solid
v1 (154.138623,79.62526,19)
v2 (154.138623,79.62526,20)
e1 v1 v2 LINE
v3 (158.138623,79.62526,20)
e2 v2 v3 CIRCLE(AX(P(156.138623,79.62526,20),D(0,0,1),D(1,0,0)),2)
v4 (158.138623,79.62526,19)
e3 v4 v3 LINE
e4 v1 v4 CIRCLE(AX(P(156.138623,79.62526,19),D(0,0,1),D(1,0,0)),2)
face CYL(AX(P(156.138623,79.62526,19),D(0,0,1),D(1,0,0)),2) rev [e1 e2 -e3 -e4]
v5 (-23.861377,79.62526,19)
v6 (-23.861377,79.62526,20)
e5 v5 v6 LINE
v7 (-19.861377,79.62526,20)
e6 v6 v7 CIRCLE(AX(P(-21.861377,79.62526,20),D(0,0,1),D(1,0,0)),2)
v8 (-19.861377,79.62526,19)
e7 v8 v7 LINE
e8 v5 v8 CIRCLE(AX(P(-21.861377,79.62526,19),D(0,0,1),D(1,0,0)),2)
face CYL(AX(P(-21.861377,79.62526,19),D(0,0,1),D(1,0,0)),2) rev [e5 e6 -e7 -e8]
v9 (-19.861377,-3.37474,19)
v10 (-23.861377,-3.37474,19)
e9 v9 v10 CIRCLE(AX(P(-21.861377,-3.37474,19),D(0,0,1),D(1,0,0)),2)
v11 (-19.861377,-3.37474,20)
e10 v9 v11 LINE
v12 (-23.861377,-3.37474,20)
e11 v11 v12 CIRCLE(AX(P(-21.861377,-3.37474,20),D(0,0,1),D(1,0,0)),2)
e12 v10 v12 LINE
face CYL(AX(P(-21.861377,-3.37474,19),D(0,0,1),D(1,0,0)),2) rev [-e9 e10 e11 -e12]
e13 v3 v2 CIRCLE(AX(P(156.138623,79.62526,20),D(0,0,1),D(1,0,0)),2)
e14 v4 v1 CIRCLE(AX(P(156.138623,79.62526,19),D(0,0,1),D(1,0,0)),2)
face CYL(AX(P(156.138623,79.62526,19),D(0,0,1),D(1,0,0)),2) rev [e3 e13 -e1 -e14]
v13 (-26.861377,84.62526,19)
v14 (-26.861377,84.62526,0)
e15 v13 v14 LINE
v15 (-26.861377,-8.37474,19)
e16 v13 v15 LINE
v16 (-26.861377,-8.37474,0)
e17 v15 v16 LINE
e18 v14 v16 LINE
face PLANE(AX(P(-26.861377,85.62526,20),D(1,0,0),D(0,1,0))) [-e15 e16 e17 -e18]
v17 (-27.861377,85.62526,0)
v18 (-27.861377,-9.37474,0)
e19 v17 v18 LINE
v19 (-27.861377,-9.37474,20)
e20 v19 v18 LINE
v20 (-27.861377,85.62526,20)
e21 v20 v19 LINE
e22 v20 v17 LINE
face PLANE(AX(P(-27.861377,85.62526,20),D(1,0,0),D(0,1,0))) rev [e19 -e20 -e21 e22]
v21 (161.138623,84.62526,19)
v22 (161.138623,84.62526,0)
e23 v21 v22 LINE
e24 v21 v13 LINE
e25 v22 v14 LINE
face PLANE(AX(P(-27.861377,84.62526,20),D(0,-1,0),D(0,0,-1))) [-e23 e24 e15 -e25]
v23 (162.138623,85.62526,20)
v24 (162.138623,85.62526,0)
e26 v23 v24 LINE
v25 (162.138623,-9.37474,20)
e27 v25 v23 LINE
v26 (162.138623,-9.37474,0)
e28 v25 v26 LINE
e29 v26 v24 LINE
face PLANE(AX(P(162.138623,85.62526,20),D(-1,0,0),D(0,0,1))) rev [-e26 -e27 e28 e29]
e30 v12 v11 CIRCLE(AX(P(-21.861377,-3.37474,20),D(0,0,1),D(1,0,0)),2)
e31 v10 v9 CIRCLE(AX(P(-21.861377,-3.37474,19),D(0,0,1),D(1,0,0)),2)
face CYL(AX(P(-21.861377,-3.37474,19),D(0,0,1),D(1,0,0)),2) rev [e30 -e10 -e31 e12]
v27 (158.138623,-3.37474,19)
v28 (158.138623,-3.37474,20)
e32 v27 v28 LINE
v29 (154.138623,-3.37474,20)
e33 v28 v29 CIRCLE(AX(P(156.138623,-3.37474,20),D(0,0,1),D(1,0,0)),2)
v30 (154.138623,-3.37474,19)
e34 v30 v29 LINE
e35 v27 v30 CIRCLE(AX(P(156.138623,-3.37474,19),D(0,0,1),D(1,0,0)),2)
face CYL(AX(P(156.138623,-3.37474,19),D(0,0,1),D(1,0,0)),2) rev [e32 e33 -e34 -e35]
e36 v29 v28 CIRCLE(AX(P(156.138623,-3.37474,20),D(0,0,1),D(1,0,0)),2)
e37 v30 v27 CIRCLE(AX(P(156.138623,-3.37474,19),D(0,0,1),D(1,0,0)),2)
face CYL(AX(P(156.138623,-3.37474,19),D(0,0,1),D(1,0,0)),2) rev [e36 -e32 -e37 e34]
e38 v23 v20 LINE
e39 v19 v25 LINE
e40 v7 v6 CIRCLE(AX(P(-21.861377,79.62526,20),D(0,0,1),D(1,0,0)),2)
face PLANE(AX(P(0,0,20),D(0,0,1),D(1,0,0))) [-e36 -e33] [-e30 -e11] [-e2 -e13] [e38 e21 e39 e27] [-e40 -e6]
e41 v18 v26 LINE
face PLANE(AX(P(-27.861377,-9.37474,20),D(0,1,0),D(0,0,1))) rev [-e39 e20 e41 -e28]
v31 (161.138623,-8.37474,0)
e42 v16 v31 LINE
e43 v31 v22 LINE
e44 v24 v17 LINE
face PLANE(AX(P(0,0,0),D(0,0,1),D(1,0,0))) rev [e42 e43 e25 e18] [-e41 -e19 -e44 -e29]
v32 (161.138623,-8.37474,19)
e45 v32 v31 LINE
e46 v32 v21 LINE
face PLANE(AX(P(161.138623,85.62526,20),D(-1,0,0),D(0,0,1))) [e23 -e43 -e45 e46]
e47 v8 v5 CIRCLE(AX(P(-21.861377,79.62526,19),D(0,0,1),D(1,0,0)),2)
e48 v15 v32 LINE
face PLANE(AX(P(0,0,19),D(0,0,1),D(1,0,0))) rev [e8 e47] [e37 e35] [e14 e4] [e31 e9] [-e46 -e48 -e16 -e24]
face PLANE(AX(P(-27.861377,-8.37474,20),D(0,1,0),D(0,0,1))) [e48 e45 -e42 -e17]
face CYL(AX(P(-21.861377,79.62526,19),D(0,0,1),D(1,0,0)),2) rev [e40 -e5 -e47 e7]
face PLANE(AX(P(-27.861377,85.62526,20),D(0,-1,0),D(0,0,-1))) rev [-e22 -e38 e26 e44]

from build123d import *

# Parameters (mm, degrees)
SKETCH1_W           = 190
SKETCH1_H           = 95
BOSS_EXTRUDE1_DEPTH = 20
SHELL1_T            = -1
SKETCH2_W           = 146
SKETCH2_H           = 10
CUT_EXTRUDE1_DEPTH  = 1
SKETCH4_R           = 3.5
SKETCH4_W           = 9
SKETCH4_H           = 5.067595116
CUT_EXTRUDE2_DEPTH  = 10
SKETCH5_W           = 3
SKETCH5_H           = 2
CUT_EXTRUDE3_DEPTH  = 1
SKETCH6_R           = 2
CUT_EXTRUDE4_DEPTH  = 1
SKETCH8_W           = 3
SKETCH8_H           = 2
SKETCH8_W_2         = 27
SKETCH8_W_3         = 7
SKETCH8_W_4         = 17
SKETCH8_W_5         = 10
CUT_EXTRUDE5_DEPTH  = 1
SKETCH9_W           = 3
SKETCH9_H           = 2
SKETCH9_W_2         = 17
SKETCH9_W_3         = 6
SKETCH9_W_4         = 14
CUT_EXTRUDE6_DEPTH  = 1
SKETCH10_W          = 146
SKETCH10_H          = 12
BOSS_EXTRUDE2_DEPTH = 1
SKETCH11_R          = 3.5
SKETCH11_W          = 156
SKETCH11_H          = 11.148334169
SKETCH11_W_2        = 9
SKETCH11_H_2        = 5.067595116
BOSS_EXTRUDE3_DEPTH = 1
SKETCH12_W          = 22.5
SKETCH12_H          = 11
BOSS_EXTRUDE4_DEPTH = 1


with BuildPart() as part:
    # Sketch1 → Boss-Extrude1 (new body)
    with BuildSketch(Plane.XY):
        with Locations((67.138623448, 38.125260091)):
            Rectangle(SKETCH1_W, SKETCH1_H)
    extrude(amount=BOSS_EXTRUDE1_DEPTH)

    # Shell1
    shell1_openings = [part.faces().sort_by_distance(p)[0] for p in [
        (67.138623448, 38.125260091, 0),
    ]]
    offset(amount=SHELL1_T, openings=shell1_openings, kind=Kind.INTERSECTION)

    # Sketch2 → Cut-Extrude1 (cut)
    with BuildSketch(Plane(origin=(0, 85.625260091, 0), x_dir=(1, 0, 0), z_dir=(0, 1, 0))):
        Polygon((139.138623448, -9), (139.138623448, -8), (139.638623448, -8), (149.638623448, -8), (149.638623448, -19), (139.638623448, -19), (139.138623448, -19), (127.138623448, -19), (127.138623448, -9), align=None)
        with Locations((53.138623448, -14)):
            Rectangle(SKETCH2_W, SKETCH2_H)
    extrude(amount=-CUT_EXTRUDE1_DEPTH, mode=Mode.SUBTRACT)

    # Sketch4 → Cut-Extrude2 (cut)
    with BuildSketch(Plane.XZ.offset(9.374739909)):
        with Locations(Location((144.138623448, 6.5, 0), (0, 0, 270))):
            Circle(SKETCH4_R)
        Polygon((124.166122212, 9.851665831), (138.166122212, 9.851665831), (138.166122212, 19), (-17.833877788, 19), (-17.833877788, 9.851665831), (-14.833877788, 9.851665831), (-14.833877788, 7.851665831), (-11.833877788, 7.851665831), (-11.833877788, 9.851665831), (5.166122212, 9.851665831), (5.166122212, 7.851665831), (8.166122212, 7.851665831), (8.166122212, 9.851665831), (14.166122212, 9.851665831), (14.166122212, 7.851665831), (17.166122212, 7.851665831), (17.166122212, 9.851665831), (34.166122212, 9.851665831), (34.166122212, 7.851665831), (37.166122212, 7.851665831), (37.166122212, 9.851665831), (43.166122212, 9.851665831), (43.166122212, 7.851665831), (46.166122212, 7.851665831), (46.166122212, 9.851665831), (63.166122212, 9.851665831), (63.166122212, 7.851665831), (66.166122212, 7.851665831), (66.166122212, 9.851665831), (72.166122212, 9.851665831), (72.166122212, 7.851665831), (75.166122212, 7.851665831), (75.166122212, 9.851665831), (92.166122212, 9.851665831), (92.166122212, 7.851665831), (95.166122212, 7.851665831), (95.166122212, 9.851665831), (101.166122212, 9.851665831), (101.166122212, 7.851665831), (104.166122212, 7.851665831), (104.166122212, 9.851665831), (121.166122212, 9.851665831), (121.166122212, 7.851665831), (124.166122212, 7.851665831), align=None)
        with Locations((109.666122212, 4.317868273)):
            Rectangle(SKETCH4_W, SKETCH4_H)
    extrude(amount=-CUT_EXTRUDE2_DEPTH, mode=Mode.SUBTRACT)

    # Sketch5 → Cut-Extrude3 (cut)
    with BuildSketch(Plane(origin=(0, 85.625260091, 0), x_dir=(1, 0, 0), z_dir=(0, 1, 0))):
        with Locations((-15.361376552, -8)):
            Rectangle(SKETCH5_W, SKETCH5_H)
        with Locations((14.638623448, -8)):
            Rectangle(SKETCH5_W, SKETCH5_H)
        with Locations((24.638623448, -8)):
            Rectangle(SKETCH5_W, SKETCH5_H)
        with Locations((54.638623448, -8)):
            Rectangle(SKETCH5_W, SKETCH5_H)
        with Locations((64.638623448, -8)):
            Rectangle(SKETCH5_W, SKETCH5_H)
        with Locations((84.638623448, -8)):
            Rectangle(SKETCH5_W, SKETCH5_H)
        with Locations((94.638623448, -8)):
            Rectangle(SKETCH5_W, SKETCH5_H)
        with Locations((114.638623448, -8)):
            Rectangle(SKETCH5_W, SKETCH5_H)
    extrude(amount=-CUT_EXTRUDE3_DEPTH, mode=Mode.SUBTRACT)

    # Sketch6 → Cut-Extrude4 (cut)
    with BuildSketch(Plane.XY.offset(20)):
        with Locations((-21.861376552, -3.374739909)):
            Circle(SKETCH6_R)
        with Locations((-21.861376552, 79.625260091)):
            Circle(SKETCH6_R)
        with Locations((156.138623448, 79.625260091)):
            Circle(SKETCH6_R)
        with Locations((156.138623448, -3.374739909)):
            Circle(SKETCH6_R)
    extrude(amount=-CUT_EXTRUDE4_DEPTH, mode=Mode.SUBTRACT)

    # Sketch8 → Cut-Extrude5 (cut)
    with BuildSketch(Plane(origin=(0, 85.625260091, 0), x_dir=(1, 0, 0), z_dir=(0, 1, 0))):
        with Locations((-18.361376552, -8)):
            Rectangle(SKETCH8_W, SKETCH8_H)
        with Locations((-0.361376552, -8)):
            Rectangle(SKETCH8_W_2, SKETCH8_H)
        with Locations((19.638623448, -8)):
            Rectangle(SKETCH8_W_3, SKETCH8_H)
        with Locations((39.638623448, -8)):
            Rectangle(SKETCH8_W_2, SKETCH8_H)
        with Locations((59.638623448, -8)):
            Rectangle(SKETCH8_W_3, SKETCH8_H)
        with Locations((74.638623448, -8)):
            Rectangle(SKETCH8_W_4, SKETCH8_H)
        with Locations((89.638623448, -8)):
            Rectangle(SKETCH8_W_3, SKETCH8_H)
        with Locations((104.638623448, -8)):
            Rectangle(SKETCH8_W_4, SKETCH8_H)
        with Locations((121.138623448, -8)):
            Rectangle(SKETCH8_W_5, SKETCH8_H)
    extrude(amount=-CUT_EXTRUDE5_DEPTH, mode=Mode.SUBTRACT)

    # Sketch9 → Cut-Extrude6 (cut)
    with BuildSketch(Plane.XZ.offset(9.374739909)):
        with Locations((-16.333877788, 8.851665831)):
            Rectangle(SKETCH9_W, SKETCH9_H)
        with Locations((-3.333877788, 8.851665831)):
            Rectangle(SKETCH9_W_2, SKETCH9_H)
        with Locations((11.166122212, 8.851665831)):
            Rectangle(SKETCH9_W_3, SKETCH9_H)
        with Locations((25.666122212, 8.851665831)):
            Rectangle(SKETCH9_W_2, SKETCH9_H)
        with Locations((40.166122212, 8.851665831)):
            Rectangle(SKETCH9_W_3, SKETCH9_H)
        with Locations((54.666122212, 8.851665831)):
            Rectangle(SKETCH9_W_2, SKETCH9_H)
        with Locations((69.166122212, 8.851665831)):
            Rectangle(SKETCH9_W_3, SKETCH9_H)
        with Locations((83.666122212, 8.851665831)):
            Rectangle(SKETCH9_W_2, SKETCH9_H)
        with Locations((98.166122212, 8.851665831)):
            Rectangle(SKETCH9_W_3, SKETCH9_H)
        with Locations((112.666122212, 8.851665831)):
            Rectangle(SKETCH9_W_2, SKETCH9_H)
        with Locations((131.166122212, 8.851665831)):
            Rectangle(SKETCH9_W_4, SKETCH9_H)
    extrude(amount=-CUT_EXTRUDE6_DEPTH, mode=Mode.SUBTRACT)

    # Sketch10 → Boss-Extrude2 (add)
    with BuildSketch(Plane(origin=(0, 85.625260091, 0), x_dir=(1, 0, 0), z_dir=(0, 1, 0))):
        with Locations((53.138623448, -13)):
            Rectangle(SKETCH10_W, SKETCH10_H)
    extrude(amount=-BOSS_EXTRUDE2_DEPTH)

    # Sketch11 → Boss-Extrude3 (add)
    with BuildSketch(Plane.XZ.offset(9.374739909)):
        with Locations((144.138623448, 6.5)):
            Circle(SKETCH11_R)
        with Locations((60.166122212, 13.425832916)):
            Rectangle(SKETCH11_W, SKETCH11_H)
        with Locations((109.666122212, 4.317868273)):
            Rectangle(SKETCH11_W_2, SKETCH11_H_2)
    extrude(amount=-BOSS_EXTRUDE3_DEPTH)

    # Sketch12 → Boss-Extrude4 (add)
    with BuildSketch(Plane(origin=(0, 85.625260091, 0), x_dir=(1, 0, 0), z_dir=(0, 1, 0))):
        with Locations((138.388623448, -13.5)):
            Rectangle(SKETCH12_W, SKETCH12_H)
    extrude(amount=-BOSS_EXTRUDE4_DEPTH)


solid = part.part
